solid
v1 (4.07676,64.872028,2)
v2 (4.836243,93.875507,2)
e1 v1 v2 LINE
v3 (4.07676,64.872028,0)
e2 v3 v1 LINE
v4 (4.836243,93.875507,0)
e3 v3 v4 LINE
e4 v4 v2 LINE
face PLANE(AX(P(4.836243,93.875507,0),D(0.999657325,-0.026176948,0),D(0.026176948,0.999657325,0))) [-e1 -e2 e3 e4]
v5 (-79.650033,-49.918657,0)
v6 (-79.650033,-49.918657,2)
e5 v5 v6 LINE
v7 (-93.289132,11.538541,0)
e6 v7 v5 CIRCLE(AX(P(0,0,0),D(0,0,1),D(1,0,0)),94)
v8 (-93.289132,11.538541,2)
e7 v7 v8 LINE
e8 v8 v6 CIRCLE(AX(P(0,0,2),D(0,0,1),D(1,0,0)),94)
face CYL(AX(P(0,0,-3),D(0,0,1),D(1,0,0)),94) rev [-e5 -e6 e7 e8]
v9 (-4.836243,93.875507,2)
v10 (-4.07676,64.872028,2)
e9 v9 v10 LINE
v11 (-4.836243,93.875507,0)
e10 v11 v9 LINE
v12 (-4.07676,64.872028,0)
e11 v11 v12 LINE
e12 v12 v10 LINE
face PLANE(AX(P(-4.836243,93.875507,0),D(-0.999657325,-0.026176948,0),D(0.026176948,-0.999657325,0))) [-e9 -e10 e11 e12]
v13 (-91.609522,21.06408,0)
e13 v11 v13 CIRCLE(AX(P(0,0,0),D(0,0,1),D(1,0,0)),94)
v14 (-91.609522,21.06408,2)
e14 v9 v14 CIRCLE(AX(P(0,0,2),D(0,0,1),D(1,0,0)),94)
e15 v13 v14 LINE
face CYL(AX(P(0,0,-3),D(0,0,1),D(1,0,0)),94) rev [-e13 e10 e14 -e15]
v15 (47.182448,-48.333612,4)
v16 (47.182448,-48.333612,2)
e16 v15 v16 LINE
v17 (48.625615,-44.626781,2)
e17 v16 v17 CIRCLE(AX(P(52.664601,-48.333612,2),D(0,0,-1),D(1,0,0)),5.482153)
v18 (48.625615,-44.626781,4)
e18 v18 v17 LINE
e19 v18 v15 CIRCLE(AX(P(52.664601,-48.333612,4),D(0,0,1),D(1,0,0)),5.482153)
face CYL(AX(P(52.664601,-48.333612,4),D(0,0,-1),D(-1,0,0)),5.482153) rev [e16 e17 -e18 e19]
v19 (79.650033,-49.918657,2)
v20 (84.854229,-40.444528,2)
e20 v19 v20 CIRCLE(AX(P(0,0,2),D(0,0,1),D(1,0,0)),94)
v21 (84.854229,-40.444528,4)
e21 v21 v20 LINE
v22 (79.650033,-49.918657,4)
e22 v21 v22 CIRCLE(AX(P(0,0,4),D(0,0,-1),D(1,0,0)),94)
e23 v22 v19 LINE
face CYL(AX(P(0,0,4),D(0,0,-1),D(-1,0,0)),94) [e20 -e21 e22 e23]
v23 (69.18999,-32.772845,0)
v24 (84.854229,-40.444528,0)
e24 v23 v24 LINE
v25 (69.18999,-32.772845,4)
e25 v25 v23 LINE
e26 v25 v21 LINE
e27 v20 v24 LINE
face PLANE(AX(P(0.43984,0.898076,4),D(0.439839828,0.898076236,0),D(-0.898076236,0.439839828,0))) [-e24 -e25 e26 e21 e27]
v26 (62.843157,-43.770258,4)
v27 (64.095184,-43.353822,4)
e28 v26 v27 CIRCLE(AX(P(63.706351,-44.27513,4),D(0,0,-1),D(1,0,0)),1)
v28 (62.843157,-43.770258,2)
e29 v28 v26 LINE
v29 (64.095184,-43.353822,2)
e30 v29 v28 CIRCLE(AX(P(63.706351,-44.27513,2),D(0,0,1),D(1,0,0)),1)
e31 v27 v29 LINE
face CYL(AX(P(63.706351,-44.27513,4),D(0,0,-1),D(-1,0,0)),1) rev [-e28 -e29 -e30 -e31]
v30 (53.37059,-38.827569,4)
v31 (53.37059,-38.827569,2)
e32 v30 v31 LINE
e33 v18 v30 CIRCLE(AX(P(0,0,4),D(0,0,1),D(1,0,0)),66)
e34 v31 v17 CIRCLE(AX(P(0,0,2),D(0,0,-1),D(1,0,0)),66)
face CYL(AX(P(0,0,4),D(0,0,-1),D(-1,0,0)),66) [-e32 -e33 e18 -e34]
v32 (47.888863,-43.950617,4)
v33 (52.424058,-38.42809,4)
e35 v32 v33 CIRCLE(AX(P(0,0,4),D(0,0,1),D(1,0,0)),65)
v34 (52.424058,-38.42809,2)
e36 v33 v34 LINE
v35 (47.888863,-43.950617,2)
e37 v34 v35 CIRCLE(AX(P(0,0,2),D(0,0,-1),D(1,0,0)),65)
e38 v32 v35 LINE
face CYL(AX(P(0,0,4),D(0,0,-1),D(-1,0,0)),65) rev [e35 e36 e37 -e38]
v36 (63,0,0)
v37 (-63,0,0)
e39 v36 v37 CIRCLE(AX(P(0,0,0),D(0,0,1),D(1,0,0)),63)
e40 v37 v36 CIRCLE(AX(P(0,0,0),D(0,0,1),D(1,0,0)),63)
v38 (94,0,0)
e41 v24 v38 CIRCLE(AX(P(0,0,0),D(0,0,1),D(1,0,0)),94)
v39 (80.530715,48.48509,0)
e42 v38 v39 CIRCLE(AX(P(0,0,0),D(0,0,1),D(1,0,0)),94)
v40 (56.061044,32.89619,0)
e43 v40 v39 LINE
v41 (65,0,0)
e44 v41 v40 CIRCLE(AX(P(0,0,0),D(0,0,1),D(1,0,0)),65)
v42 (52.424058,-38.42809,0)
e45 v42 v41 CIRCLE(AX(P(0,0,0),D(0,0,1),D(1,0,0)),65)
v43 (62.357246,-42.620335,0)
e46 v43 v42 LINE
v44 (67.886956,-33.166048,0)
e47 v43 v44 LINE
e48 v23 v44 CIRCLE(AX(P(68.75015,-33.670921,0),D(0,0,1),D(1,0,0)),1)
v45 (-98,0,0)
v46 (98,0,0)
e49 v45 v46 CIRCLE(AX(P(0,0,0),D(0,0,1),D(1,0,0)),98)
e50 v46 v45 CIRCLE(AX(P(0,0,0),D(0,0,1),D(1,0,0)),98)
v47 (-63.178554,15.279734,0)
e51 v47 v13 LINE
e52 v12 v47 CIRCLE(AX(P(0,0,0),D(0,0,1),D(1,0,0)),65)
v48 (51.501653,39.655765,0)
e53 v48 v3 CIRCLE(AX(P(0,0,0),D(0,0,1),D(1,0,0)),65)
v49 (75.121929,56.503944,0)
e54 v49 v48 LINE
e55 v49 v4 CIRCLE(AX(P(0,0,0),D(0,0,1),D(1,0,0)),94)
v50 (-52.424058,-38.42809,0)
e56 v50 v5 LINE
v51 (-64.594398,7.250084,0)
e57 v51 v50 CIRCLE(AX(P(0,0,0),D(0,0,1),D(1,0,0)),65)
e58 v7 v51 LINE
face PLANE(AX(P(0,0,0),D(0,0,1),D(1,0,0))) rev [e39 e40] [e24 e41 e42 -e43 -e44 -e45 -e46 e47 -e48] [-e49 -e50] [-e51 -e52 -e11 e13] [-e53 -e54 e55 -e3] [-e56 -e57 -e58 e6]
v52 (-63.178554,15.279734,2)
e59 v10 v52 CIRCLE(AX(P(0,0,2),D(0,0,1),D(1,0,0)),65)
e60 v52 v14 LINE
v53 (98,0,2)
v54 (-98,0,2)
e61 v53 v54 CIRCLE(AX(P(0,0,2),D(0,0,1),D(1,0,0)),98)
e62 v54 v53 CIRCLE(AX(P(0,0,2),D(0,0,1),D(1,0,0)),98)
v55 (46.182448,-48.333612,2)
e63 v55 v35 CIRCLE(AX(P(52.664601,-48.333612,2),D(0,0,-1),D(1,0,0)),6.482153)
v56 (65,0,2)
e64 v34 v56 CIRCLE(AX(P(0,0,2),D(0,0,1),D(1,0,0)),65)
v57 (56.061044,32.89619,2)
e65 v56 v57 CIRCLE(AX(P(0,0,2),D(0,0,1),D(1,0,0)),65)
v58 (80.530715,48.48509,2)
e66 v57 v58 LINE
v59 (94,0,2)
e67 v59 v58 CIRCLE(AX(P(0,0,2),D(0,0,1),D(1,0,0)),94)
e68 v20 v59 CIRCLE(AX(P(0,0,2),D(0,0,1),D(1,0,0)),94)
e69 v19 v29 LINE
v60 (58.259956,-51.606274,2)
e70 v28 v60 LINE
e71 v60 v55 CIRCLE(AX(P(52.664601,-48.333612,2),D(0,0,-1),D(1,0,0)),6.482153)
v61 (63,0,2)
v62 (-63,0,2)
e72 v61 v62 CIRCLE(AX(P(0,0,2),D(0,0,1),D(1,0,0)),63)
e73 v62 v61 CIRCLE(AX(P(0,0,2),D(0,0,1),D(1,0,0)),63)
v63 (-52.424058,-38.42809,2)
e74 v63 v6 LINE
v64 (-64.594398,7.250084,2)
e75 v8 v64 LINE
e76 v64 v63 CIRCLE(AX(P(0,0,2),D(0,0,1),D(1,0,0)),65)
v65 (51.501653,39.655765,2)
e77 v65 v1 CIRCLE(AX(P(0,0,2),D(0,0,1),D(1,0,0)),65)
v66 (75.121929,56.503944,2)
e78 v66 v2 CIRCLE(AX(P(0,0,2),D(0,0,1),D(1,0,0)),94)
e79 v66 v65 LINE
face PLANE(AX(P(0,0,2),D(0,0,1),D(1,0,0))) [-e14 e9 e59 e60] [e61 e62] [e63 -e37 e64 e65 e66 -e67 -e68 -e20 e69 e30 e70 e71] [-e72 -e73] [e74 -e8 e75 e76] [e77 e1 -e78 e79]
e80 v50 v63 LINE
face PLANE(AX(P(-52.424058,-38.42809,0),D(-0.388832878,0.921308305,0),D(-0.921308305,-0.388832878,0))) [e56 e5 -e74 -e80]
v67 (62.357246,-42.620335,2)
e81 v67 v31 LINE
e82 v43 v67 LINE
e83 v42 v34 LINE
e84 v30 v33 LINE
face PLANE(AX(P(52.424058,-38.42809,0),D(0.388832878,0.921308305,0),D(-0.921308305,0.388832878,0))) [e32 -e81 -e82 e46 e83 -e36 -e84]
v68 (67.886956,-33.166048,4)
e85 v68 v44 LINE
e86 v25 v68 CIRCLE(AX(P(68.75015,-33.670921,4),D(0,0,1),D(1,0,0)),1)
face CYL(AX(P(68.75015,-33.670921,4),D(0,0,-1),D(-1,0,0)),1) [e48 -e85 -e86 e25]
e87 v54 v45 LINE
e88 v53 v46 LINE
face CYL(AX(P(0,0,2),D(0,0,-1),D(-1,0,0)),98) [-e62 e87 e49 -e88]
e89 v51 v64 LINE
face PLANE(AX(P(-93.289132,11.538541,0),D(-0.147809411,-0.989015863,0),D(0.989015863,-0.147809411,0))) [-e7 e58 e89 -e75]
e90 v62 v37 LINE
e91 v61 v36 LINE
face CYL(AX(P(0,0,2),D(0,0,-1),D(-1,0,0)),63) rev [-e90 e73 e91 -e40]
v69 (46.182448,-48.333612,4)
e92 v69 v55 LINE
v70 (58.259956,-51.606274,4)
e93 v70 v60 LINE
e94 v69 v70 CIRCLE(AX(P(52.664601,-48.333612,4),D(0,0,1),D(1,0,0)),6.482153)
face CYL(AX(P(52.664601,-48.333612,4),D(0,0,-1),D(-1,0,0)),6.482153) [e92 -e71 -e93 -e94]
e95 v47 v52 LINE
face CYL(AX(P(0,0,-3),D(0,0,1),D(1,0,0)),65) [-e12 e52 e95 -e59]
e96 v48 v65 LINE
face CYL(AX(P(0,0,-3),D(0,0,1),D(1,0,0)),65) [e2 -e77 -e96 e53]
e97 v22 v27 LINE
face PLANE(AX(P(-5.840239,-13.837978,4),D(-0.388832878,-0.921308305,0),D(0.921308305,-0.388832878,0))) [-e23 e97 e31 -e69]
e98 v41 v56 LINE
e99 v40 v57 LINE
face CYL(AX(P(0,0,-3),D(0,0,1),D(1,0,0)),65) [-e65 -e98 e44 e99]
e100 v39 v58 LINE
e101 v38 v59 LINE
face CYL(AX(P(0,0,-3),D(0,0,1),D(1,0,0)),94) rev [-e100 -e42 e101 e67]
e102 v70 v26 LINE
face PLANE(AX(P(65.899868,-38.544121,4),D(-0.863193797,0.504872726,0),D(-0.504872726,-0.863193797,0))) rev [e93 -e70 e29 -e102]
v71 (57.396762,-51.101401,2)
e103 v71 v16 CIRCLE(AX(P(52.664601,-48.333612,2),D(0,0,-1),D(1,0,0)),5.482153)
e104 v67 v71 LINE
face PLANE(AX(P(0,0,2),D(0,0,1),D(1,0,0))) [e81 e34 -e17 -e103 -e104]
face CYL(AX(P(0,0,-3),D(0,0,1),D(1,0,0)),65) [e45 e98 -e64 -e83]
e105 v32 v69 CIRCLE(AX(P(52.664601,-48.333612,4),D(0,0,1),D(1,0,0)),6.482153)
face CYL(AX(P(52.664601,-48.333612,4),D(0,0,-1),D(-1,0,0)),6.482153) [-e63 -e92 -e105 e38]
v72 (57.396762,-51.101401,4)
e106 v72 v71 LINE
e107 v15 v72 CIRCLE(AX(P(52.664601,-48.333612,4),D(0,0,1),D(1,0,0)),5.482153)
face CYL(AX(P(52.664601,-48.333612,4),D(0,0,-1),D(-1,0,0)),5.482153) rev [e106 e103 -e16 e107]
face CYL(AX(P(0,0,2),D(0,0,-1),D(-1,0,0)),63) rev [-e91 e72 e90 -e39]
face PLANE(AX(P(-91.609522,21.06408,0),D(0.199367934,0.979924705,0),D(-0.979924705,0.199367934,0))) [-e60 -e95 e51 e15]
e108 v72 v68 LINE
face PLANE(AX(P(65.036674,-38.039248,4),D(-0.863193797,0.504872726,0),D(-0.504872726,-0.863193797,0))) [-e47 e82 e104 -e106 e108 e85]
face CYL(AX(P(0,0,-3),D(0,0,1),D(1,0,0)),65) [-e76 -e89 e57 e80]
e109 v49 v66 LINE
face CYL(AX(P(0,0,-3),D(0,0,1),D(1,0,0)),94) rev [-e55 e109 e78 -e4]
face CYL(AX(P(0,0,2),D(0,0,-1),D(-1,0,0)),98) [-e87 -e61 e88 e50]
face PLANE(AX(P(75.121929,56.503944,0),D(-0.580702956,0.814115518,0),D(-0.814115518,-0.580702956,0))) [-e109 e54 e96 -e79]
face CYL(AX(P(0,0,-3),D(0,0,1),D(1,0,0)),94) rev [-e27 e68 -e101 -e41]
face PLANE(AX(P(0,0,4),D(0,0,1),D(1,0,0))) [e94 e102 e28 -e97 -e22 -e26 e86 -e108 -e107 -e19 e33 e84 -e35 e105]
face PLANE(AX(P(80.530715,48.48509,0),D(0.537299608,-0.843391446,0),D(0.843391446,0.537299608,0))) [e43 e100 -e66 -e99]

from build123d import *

# Parameters (mm, degrees)
SKETCH1_R           = 98
SKETCH1_R_2         = 63
BOSS_EXTRUDE1_DEPTH = 2
SKETCH2_R           = 94
SKETCH2_R_2         = 65
CUT_EXTRUDE2_DEPTH  = 5
BOSS_EXTRUDE2_DEPTH = 2
BOSS_EXTRUDE7_DEPTH = 2
BOSS_EXTRUDE9_DEPTH = 2
FILLET1_R           = 1


with BuildPart() as part:
    # Sketch1 → Boss-Extrude1 (new body)
    with BuildSketch(Plane.XY):
        Circle(SKETCH1_R)
        Circle(SKETCH1_R_2, mode=Mode.SUBTRACT)
    extrude(amount=BOSS_EXTRUDE1_DEPTH)

    # Sketch2 → Cut-Extrude2 (cut)
    with BuildSketch(Plane.XY.offset(2)):
        Circle(SKETCH2_R)
        Circle(SKETCH2_R_2, mode=Mode.SUBTRACT)
    extrude(amount=-CUT_EXTRUDE2_DEPTH, mode=Mode.SUBTRACT)


with BuildPart() as cut_extrude2_piece_1:
    # of the separate pieces the step leaves, piece 1, a body of its own (cut_extrude2_pieces)
    add(part.part.solids().sort_by_distance((98, 0, 0))[0])



with BuildPart() as cut_extrude2_piece_2:
    # of the separate pieces the step leaves, piece 2, a body of its own (cut_extrude2_pieces)
    add(part.part.solids().sort_by_distance((65, 0, 0))[0])


with BuildPart() as cut_extrude2_piece_1_1:
    add(cut_extrude2_piece_1.part)

    add(cut_extrude2_piece_2.part)  # Boss-Extrude2 merges Cut-Extrude2 piece 2
    # Sketch3 → Boss-Extrude2 (add)
    with BuildSketch(Plane.XY.offset(2)):
        with BuildLine():
            Line((4.836242993, 93.875506676), (4.076760177, 64.872028074))
            ThreePointArc((4.076760177, 64.872028074), (0, 65), (-4.076760177, 64.872028074))
            Line((-4.076760177, 64.872028074), (-4.836242993, 93.875506676))
            ThreePointArc((-4.836242993, 93.875506676), (0, 94), (4.836242993, 93.875506676))
        make_face()
        with BuildLine():
            Line((75.121929416, 56.503944294), (51.501653321, 39.655765094))
            ThreePointArc((51.501653321, 39.655765094), (53.887442216, 36.347538726), (56.061044042, 32.896190372))
            Line((56.061044042, 32.896190372), (80.530714938, 48.485089992))
            ThreePointArc((80.530714938, 48.485089992), (77.92953182, 52.564132926), (75.121929416, 56.503944294))
        make_face()
        with BuildLine():
            Line((-93.289131575, 11.538541067), (-64.594398177, 7.250084427))
            ThreePointArc((-64.594398177, 7.250084427), (-64.012503946, 11.287131548), (-63.178554226, 15.279734486))
            Line((-63.178554226, 15.279734486), (-91.60952201, 21.064080257))
            ThreePointArc((-91.60952201, 21.064080257), (-92.571928783, 16.322928701), (-93.289131575, 11.538541067))
        make_face()
    extrude(amount=-BOSS_EXTRUDE2_DEPTH)

    # Sketch8 → Boss-Extrude7 (add)
    with BuildSketch(Plane.XY.offset(2)):
        with BuildLine():
            Line((-52.42405813, -38.428090366), (-79.6500328, -49.918656582))
            ThreePointArc((-79.6500328, -49.918656582), (0, -94), (79.6500328, -49.918656582))
            Line((79.6500328, -49.918656582), (52.42405813, -38.428090366))
            ThreePointArc((52.42405813, -38.428090366), (0, -65), (-52.42405813, -38.428090366))
        make_face()
    extrude(amount=-BOSS_EXTRUDE7_DEPTH)

    # Sketch9 → Boss-Extrude9 (add, symmetric)
    with BuildSketch(Plane.XY.offset(2)):
        with BuildLine():
            Line((68.281233408, -34.472640013), (63.286378857, -43.012470433))
            Line((63.286378857, -43.012470433), (79.6500328, -49.918656582))
            ThreePointArc((79.6500328, -49.918656582), (82.146531581, -45.694062516), (84.419166177, -41.344943851))
            Line((84.419166177, -41.344943851), (69.584267033, -34.079436503))
            ThreePointArc((69.584267033, -34.079436503), (68.855533807, -34.020151468), (68.281233408, -34.472640013))
        make_face()
        with BuildLine():
            Line((67.88695627, -33.166048499), (62.357246072, -42.620335278))
            Line((62.357246072, -42.620335278), (63.286378857, -43.012470433))
            Line((63.286378857, -43.012470433), (68.281233408, -34.472640013))
            ThreePointArc((68.281233408, -34.472640013), (68.855533807, -34.020151468), (69.584267033, -34.079436503))
            Line((69.584267033, -34.079436503), (84.419166177, -41.344943851))
            ThreePointArc((84.419166177, -41.344943851), (84.63789491, -40.895314466), (84.854228869, -40.444527975))
            Line((84.854228869, -40.444527975), (69.189989894, -32.772844989))
            ThreePointArc((69.189989894, -32.772844989), (68.461256668, -32.713559953), (67.88695627, -33.166048499))
        make_face()
        with BuildLine():
            Line((62.357246072, -42.620335278), (57.396762094, -51.10140145))
            ThreePointArc((57.396762094, -51.10140145), (49.408790851, -52.744247062), (48.625615223, -44.626780572))
            ThreePointArc((48.625615223, -44.626780572), (51.08046785, -41.794566683), (53.370590226, -38.8275688))
            Line((53.370590226, -38.8275688), (52.42405813, -38.428090366))
            ThreePointArc((52.42405813, -38.428090366), (50.232411211, -41.251725587), (47.888863477, -43.95061723))
            ThreePointArc((47.888863477, -43.95061723), (48.814898229, -53.548791376), (58.259955891, -51.606274177))
            Line((58.259955891, -51.606274177), (63.286378857, -43.012470433))
            Line((63.286378857, -43.012470433), (62.357246072, -42.620335278))
        make_face()
    extrude(amount=BOSS_EXTRUDE9_DEPTH, both=True)

    # Fillet1
    fillet1_edges = [cut_extrude2_piece_1_1.edges().sort_by_distance(p)[0] for p in [
        (63.286378857, -43.012470433, 3),
    ]]
    fillet(fillet1_edges, radius=FILLET1_R)


solid = cut_extrude2_piece_1_1.part
